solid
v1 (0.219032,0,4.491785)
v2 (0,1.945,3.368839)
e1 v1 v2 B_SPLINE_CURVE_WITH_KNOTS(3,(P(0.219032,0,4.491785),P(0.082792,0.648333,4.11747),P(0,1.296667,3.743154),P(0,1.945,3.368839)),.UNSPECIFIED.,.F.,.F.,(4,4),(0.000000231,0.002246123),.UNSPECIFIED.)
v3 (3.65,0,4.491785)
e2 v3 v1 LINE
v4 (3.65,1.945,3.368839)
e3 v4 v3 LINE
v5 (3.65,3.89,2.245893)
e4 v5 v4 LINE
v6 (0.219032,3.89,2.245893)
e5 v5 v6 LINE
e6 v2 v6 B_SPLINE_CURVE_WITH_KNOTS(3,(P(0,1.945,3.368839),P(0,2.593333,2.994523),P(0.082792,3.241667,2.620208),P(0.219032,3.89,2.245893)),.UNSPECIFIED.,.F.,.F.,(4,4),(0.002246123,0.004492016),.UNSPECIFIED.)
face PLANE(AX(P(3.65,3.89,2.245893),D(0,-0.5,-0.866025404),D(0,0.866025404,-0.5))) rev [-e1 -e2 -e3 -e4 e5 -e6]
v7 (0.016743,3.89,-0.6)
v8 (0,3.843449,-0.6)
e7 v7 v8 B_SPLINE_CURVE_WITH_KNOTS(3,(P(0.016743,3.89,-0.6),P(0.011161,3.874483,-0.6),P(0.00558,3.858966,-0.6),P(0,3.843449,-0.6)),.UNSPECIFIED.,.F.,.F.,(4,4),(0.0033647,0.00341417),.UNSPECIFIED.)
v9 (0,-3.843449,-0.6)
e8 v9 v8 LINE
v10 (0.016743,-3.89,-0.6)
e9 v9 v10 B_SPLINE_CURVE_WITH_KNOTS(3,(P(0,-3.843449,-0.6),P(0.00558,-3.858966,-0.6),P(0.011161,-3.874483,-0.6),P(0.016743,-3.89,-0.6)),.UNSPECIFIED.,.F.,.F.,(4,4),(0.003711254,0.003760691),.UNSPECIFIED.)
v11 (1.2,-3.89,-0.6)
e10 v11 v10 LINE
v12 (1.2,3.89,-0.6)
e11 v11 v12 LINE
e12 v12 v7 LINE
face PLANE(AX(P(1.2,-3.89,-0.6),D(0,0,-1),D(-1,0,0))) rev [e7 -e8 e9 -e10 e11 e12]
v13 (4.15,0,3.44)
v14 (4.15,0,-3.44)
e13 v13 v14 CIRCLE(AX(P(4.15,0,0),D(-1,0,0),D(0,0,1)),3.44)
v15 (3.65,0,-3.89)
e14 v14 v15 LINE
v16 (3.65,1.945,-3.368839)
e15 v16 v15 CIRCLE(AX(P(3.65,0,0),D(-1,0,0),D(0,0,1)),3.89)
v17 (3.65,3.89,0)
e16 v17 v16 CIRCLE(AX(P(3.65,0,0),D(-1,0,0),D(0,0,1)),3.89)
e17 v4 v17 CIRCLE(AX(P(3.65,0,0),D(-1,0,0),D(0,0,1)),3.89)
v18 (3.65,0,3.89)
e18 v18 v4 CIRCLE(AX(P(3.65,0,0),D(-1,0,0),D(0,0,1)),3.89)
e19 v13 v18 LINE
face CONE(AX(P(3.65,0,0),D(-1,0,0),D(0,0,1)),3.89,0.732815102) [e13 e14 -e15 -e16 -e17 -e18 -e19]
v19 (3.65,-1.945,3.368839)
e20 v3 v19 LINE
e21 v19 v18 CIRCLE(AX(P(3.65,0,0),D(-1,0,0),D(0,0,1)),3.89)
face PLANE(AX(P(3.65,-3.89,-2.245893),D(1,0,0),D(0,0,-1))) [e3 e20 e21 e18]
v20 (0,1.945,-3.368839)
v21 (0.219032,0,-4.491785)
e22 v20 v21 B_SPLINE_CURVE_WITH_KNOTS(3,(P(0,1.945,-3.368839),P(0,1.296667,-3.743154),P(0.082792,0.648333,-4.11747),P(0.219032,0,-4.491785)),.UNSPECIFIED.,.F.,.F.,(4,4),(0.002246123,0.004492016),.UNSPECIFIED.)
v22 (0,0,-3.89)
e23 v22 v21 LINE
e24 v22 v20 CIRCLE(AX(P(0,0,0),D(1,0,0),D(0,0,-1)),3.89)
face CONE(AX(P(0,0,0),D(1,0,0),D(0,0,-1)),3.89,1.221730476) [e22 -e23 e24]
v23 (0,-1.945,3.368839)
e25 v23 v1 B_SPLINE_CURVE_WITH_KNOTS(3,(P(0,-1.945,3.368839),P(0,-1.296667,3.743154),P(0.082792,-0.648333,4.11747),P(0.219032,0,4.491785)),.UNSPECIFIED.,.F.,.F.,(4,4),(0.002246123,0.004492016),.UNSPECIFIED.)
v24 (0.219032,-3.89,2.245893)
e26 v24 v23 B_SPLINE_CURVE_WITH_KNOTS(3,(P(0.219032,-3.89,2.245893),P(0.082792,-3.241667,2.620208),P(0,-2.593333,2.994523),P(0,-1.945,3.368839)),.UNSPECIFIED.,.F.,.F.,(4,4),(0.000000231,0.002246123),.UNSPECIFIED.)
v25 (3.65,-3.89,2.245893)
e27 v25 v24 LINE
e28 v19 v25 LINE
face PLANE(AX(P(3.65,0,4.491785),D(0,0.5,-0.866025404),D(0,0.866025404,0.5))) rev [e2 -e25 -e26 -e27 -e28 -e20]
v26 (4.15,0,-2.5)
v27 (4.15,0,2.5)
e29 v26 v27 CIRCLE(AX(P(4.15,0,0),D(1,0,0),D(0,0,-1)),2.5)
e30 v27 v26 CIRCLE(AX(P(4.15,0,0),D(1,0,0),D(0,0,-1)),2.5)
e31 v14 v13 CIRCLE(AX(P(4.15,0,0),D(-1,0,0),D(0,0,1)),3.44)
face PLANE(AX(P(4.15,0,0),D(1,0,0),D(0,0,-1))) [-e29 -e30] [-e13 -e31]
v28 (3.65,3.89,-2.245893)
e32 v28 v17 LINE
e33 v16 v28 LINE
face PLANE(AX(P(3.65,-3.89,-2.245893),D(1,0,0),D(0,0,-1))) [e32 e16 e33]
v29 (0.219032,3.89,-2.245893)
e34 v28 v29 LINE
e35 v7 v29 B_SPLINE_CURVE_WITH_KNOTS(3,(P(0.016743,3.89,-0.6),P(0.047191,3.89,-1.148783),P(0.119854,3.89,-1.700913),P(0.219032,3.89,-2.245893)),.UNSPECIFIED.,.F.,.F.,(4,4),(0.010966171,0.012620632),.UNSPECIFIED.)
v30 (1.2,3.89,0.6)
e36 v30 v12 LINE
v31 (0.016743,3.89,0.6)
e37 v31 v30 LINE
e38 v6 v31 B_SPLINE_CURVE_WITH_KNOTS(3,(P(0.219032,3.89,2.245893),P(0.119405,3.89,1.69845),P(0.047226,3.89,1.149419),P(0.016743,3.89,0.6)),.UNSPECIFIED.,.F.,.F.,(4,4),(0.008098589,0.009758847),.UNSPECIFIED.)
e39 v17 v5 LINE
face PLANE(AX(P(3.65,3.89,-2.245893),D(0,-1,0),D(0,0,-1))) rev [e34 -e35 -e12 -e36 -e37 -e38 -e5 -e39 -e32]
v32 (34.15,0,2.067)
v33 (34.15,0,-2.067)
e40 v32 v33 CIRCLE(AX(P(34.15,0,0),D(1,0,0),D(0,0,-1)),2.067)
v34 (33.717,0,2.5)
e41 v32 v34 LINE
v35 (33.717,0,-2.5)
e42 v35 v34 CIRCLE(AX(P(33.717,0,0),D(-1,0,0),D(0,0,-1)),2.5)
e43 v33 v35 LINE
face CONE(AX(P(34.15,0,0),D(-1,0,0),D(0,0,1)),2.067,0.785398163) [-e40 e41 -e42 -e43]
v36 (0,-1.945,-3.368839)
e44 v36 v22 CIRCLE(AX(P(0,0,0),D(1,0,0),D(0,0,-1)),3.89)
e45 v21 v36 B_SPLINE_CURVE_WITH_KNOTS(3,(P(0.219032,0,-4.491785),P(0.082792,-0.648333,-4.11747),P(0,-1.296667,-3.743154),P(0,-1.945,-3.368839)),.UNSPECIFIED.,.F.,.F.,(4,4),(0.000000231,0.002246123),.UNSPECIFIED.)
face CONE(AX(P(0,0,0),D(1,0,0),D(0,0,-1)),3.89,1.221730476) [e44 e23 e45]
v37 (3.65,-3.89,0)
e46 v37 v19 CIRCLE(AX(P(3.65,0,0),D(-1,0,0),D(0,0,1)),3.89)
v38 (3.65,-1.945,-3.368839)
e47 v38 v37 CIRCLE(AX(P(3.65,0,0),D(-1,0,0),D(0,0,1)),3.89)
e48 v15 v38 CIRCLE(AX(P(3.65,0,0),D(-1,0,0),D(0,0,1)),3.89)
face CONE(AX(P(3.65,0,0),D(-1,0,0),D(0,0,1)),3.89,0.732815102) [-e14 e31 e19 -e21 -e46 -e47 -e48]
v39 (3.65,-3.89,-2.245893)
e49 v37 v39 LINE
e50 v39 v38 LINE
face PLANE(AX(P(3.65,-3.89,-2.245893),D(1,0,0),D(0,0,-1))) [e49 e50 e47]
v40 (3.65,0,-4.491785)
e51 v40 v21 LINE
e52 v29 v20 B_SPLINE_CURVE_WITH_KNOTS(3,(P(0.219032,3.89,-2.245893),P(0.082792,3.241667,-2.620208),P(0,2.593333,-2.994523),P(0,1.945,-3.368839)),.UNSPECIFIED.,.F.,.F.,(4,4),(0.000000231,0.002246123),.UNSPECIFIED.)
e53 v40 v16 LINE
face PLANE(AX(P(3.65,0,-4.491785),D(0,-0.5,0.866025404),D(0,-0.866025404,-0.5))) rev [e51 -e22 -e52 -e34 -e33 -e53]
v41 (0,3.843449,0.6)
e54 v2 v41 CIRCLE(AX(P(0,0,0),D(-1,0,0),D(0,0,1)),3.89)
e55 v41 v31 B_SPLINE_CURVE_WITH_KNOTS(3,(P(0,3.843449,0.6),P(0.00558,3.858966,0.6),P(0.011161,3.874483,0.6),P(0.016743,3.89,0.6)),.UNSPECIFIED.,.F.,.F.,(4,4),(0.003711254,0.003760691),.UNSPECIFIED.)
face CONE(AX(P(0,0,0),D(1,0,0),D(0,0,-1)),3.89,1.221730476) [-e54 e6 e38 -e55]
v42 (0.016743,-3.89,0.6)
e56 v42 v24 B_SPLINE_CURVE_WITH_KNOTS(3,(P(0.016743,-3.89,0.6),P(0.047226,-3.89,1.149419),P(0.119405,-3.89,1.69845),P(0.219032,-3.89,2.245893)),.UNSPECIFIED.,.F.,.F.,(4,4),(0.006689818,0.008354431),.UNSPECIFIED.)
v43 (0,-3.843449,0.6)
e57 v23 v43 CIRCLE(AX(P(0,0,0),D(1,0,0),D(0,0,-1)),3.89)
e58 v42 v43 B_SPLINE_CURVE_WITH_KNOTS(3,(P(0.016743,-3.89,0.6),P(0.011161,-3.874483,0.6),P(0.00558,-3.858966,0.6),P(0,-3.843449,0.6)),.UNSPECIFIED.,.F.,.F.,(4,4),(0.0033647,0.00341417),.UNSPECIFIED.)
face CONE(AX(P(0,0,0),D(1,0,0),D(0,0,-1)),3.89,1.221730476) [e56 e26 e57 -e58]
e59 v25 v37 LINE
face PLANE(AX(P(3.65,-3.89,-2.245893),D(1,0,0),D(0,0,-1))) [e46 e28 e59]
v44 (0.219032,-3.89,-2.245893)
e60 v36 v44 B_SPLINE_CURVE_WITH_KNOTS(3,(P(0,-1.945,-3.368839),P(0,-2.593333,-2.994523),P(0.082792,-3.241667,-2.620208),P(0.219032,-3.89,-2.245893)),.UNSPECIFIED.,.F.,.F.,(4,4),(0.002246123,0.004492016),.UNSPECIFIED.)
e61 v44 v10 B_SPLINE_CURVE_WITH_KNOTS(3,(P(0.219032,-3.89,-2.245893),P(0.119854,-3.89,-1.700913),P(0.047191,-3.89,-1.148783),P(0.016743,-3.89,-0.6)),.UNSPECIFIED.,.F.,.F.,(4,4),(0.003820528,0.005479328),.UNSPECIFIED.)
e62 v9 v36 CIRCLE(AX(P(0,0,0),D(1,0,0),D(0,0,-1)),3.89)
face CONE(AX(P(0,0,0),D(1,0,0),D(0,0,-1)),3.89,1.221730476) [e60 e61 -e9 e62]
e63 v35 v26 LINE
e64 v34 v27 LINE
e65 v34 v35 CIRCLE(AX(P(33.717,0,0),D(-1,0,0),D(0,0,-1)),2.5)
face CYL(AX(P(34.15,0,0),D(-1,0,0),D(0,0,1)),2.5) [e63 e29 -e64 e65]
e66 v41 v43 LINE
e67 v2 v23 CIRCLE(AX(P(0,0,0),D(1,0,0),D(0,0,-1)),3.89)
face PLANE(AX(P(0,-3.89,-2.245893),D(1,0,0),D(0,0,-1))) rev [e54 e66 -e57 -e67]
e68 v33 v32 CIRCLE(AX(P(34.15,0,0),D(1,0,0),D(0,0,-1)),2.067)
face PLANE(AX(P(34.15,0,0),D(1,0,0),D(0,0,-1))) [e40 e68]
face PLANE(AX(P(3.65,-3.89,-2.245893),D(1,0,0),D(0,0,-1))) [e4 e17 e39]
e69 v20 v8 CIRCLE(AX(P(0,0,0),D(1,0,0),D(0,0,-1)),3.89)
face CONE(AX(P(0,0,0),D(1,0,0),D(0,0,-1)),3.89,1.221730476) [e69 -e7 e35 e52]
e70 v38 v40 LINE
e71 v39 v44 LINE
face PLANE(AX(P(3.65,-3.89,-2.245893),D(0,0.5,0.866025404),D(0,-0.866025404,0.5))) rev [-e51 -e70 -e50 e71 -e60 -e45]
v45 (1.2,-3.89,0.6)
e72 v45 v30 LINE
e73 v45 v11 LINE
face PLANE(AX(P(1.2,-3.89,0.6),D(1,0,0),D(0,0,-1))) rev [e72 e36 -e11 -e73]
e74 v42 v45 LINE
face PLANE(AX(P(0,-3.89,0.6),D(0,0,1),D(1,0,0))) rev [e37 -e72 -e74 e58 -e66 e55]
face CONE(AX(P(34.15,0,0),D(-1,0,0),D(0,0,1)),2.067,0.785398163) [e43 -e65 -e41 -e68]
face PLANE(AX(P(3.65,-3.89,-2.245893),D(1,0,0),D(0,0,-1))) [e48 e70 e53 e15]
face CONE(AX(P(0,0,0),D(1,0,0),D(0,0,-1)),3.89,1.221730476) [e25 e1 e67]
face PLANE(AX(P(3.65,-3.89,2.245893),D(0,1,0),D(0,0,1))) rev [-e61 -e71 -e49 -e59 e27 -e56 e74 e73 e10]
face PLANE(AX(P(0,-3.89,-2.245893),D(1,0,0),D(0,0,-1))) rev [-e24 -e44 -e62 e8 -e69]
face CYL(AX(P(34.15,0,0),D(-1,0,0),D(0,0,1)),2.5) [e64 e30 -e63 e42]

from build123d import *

# Parameters (mm, degrees)
BASEHEAD_DEPTH  = 3.65
SKETCH3_R       = 2.5
BASEBODY_DEPTH  = 30
CHAMFER1_SIZE   = 0.433
SLOT_DEPTH      = 35.663103343
SLOT_DEPTH_BACK = 35.663103343
SKETCH5_W       = 1.2
SKETCH5_H       = 1.2


with BuildPart() as part:
    # Sketch-BaseHead → BaseHead (new body)
    with BuildSketch(Plane(origin=(0, 0, 0), x_dir=(0, 0, -1), z_dir=(1, 0, 0))):
        Polygon((2.245892547, -3.89), (4.491785094, 0), (2.245892547, 3.89), (-2.245892547, 3.89), (-4.491785094, 0), (-2.245892547, -3.89), align=None)
    extrude(amount=BASEHEAD_DEPTH)

    # Sketch1 → Revolve1 (revolve)
    with BuildSketch(Plane.XY, mode=Mode.PRIVATE) as revolve1_sk:
        Polygon((3.65, 0), (4.15, 0), (4.15, -3.44), (3.65, -3.89), align=None)
    revolve(revolve1_sk.sketch.rotate(Axis((-4.001564945, 0, 0), (1, 0, 0)), 270), axis=Axis((-4.001564945, 0, 0), (1, 0, 0)))

    # Sketch3 → BaseBody (add)
    with BuildSketch(Plane(origin=(4.15, 0, 0), x_dir=(0, 0, -1), z_dir=(1, 0, 0))):
        Circle(SKETCH3_R)
    extrude(amount=BASEBODY_DEPTH)

    # Chamfer1
    chamfer1_edges = [part.edges().sort_by_distance(p)[0] for p in [
        (34.15, 0, 2.5),
    ]]
    chamfer(chamfer1_edges, length=CHAMFER1_SIZE)

    # Sketch4 → HeadChamfer (revolve, cut)
    with BuildSketch(Plane(origin=(-0.264637255, 0, 5.916896391), x_dir=(0, 0, -1), z_dir=(0, 1, 0)), mode=Mode.PRIVATE) as headchamfer_sk:
        Polygon((10.408681485, -0.264637255), (9.806896391, -0.264637255), (10.408681485, -0.483669117), align=None)
    revolve(headchamfer_sk.sketch.rotate(Axis((-4.001564945, 0, 0), (1, 0, 0)), 180), axis=Axis((-4.001564945, 0, 0), (1, 0, 0)), mode=Mode.SUBTRACT)

    # Sketch5 → Slot (cut, two sides: drawn at the far end of the back side and taken through both)
    with BuildSketch(Plane(origin=(0, 0, 0), x_dir=(1, 0, 0), z_dir=(0, 1, 0)).offset(-SLOT_DEPTH_BACK)):
        with Locations((0.6, 0)):
            Rectangle(SKETCH5_W, SKETCH5_H)
    extrude(amount=SLOT_DEPTH + SLOT_DEPTH_BACK, mode=Mode.SUBTRACT)


solid = part.part
